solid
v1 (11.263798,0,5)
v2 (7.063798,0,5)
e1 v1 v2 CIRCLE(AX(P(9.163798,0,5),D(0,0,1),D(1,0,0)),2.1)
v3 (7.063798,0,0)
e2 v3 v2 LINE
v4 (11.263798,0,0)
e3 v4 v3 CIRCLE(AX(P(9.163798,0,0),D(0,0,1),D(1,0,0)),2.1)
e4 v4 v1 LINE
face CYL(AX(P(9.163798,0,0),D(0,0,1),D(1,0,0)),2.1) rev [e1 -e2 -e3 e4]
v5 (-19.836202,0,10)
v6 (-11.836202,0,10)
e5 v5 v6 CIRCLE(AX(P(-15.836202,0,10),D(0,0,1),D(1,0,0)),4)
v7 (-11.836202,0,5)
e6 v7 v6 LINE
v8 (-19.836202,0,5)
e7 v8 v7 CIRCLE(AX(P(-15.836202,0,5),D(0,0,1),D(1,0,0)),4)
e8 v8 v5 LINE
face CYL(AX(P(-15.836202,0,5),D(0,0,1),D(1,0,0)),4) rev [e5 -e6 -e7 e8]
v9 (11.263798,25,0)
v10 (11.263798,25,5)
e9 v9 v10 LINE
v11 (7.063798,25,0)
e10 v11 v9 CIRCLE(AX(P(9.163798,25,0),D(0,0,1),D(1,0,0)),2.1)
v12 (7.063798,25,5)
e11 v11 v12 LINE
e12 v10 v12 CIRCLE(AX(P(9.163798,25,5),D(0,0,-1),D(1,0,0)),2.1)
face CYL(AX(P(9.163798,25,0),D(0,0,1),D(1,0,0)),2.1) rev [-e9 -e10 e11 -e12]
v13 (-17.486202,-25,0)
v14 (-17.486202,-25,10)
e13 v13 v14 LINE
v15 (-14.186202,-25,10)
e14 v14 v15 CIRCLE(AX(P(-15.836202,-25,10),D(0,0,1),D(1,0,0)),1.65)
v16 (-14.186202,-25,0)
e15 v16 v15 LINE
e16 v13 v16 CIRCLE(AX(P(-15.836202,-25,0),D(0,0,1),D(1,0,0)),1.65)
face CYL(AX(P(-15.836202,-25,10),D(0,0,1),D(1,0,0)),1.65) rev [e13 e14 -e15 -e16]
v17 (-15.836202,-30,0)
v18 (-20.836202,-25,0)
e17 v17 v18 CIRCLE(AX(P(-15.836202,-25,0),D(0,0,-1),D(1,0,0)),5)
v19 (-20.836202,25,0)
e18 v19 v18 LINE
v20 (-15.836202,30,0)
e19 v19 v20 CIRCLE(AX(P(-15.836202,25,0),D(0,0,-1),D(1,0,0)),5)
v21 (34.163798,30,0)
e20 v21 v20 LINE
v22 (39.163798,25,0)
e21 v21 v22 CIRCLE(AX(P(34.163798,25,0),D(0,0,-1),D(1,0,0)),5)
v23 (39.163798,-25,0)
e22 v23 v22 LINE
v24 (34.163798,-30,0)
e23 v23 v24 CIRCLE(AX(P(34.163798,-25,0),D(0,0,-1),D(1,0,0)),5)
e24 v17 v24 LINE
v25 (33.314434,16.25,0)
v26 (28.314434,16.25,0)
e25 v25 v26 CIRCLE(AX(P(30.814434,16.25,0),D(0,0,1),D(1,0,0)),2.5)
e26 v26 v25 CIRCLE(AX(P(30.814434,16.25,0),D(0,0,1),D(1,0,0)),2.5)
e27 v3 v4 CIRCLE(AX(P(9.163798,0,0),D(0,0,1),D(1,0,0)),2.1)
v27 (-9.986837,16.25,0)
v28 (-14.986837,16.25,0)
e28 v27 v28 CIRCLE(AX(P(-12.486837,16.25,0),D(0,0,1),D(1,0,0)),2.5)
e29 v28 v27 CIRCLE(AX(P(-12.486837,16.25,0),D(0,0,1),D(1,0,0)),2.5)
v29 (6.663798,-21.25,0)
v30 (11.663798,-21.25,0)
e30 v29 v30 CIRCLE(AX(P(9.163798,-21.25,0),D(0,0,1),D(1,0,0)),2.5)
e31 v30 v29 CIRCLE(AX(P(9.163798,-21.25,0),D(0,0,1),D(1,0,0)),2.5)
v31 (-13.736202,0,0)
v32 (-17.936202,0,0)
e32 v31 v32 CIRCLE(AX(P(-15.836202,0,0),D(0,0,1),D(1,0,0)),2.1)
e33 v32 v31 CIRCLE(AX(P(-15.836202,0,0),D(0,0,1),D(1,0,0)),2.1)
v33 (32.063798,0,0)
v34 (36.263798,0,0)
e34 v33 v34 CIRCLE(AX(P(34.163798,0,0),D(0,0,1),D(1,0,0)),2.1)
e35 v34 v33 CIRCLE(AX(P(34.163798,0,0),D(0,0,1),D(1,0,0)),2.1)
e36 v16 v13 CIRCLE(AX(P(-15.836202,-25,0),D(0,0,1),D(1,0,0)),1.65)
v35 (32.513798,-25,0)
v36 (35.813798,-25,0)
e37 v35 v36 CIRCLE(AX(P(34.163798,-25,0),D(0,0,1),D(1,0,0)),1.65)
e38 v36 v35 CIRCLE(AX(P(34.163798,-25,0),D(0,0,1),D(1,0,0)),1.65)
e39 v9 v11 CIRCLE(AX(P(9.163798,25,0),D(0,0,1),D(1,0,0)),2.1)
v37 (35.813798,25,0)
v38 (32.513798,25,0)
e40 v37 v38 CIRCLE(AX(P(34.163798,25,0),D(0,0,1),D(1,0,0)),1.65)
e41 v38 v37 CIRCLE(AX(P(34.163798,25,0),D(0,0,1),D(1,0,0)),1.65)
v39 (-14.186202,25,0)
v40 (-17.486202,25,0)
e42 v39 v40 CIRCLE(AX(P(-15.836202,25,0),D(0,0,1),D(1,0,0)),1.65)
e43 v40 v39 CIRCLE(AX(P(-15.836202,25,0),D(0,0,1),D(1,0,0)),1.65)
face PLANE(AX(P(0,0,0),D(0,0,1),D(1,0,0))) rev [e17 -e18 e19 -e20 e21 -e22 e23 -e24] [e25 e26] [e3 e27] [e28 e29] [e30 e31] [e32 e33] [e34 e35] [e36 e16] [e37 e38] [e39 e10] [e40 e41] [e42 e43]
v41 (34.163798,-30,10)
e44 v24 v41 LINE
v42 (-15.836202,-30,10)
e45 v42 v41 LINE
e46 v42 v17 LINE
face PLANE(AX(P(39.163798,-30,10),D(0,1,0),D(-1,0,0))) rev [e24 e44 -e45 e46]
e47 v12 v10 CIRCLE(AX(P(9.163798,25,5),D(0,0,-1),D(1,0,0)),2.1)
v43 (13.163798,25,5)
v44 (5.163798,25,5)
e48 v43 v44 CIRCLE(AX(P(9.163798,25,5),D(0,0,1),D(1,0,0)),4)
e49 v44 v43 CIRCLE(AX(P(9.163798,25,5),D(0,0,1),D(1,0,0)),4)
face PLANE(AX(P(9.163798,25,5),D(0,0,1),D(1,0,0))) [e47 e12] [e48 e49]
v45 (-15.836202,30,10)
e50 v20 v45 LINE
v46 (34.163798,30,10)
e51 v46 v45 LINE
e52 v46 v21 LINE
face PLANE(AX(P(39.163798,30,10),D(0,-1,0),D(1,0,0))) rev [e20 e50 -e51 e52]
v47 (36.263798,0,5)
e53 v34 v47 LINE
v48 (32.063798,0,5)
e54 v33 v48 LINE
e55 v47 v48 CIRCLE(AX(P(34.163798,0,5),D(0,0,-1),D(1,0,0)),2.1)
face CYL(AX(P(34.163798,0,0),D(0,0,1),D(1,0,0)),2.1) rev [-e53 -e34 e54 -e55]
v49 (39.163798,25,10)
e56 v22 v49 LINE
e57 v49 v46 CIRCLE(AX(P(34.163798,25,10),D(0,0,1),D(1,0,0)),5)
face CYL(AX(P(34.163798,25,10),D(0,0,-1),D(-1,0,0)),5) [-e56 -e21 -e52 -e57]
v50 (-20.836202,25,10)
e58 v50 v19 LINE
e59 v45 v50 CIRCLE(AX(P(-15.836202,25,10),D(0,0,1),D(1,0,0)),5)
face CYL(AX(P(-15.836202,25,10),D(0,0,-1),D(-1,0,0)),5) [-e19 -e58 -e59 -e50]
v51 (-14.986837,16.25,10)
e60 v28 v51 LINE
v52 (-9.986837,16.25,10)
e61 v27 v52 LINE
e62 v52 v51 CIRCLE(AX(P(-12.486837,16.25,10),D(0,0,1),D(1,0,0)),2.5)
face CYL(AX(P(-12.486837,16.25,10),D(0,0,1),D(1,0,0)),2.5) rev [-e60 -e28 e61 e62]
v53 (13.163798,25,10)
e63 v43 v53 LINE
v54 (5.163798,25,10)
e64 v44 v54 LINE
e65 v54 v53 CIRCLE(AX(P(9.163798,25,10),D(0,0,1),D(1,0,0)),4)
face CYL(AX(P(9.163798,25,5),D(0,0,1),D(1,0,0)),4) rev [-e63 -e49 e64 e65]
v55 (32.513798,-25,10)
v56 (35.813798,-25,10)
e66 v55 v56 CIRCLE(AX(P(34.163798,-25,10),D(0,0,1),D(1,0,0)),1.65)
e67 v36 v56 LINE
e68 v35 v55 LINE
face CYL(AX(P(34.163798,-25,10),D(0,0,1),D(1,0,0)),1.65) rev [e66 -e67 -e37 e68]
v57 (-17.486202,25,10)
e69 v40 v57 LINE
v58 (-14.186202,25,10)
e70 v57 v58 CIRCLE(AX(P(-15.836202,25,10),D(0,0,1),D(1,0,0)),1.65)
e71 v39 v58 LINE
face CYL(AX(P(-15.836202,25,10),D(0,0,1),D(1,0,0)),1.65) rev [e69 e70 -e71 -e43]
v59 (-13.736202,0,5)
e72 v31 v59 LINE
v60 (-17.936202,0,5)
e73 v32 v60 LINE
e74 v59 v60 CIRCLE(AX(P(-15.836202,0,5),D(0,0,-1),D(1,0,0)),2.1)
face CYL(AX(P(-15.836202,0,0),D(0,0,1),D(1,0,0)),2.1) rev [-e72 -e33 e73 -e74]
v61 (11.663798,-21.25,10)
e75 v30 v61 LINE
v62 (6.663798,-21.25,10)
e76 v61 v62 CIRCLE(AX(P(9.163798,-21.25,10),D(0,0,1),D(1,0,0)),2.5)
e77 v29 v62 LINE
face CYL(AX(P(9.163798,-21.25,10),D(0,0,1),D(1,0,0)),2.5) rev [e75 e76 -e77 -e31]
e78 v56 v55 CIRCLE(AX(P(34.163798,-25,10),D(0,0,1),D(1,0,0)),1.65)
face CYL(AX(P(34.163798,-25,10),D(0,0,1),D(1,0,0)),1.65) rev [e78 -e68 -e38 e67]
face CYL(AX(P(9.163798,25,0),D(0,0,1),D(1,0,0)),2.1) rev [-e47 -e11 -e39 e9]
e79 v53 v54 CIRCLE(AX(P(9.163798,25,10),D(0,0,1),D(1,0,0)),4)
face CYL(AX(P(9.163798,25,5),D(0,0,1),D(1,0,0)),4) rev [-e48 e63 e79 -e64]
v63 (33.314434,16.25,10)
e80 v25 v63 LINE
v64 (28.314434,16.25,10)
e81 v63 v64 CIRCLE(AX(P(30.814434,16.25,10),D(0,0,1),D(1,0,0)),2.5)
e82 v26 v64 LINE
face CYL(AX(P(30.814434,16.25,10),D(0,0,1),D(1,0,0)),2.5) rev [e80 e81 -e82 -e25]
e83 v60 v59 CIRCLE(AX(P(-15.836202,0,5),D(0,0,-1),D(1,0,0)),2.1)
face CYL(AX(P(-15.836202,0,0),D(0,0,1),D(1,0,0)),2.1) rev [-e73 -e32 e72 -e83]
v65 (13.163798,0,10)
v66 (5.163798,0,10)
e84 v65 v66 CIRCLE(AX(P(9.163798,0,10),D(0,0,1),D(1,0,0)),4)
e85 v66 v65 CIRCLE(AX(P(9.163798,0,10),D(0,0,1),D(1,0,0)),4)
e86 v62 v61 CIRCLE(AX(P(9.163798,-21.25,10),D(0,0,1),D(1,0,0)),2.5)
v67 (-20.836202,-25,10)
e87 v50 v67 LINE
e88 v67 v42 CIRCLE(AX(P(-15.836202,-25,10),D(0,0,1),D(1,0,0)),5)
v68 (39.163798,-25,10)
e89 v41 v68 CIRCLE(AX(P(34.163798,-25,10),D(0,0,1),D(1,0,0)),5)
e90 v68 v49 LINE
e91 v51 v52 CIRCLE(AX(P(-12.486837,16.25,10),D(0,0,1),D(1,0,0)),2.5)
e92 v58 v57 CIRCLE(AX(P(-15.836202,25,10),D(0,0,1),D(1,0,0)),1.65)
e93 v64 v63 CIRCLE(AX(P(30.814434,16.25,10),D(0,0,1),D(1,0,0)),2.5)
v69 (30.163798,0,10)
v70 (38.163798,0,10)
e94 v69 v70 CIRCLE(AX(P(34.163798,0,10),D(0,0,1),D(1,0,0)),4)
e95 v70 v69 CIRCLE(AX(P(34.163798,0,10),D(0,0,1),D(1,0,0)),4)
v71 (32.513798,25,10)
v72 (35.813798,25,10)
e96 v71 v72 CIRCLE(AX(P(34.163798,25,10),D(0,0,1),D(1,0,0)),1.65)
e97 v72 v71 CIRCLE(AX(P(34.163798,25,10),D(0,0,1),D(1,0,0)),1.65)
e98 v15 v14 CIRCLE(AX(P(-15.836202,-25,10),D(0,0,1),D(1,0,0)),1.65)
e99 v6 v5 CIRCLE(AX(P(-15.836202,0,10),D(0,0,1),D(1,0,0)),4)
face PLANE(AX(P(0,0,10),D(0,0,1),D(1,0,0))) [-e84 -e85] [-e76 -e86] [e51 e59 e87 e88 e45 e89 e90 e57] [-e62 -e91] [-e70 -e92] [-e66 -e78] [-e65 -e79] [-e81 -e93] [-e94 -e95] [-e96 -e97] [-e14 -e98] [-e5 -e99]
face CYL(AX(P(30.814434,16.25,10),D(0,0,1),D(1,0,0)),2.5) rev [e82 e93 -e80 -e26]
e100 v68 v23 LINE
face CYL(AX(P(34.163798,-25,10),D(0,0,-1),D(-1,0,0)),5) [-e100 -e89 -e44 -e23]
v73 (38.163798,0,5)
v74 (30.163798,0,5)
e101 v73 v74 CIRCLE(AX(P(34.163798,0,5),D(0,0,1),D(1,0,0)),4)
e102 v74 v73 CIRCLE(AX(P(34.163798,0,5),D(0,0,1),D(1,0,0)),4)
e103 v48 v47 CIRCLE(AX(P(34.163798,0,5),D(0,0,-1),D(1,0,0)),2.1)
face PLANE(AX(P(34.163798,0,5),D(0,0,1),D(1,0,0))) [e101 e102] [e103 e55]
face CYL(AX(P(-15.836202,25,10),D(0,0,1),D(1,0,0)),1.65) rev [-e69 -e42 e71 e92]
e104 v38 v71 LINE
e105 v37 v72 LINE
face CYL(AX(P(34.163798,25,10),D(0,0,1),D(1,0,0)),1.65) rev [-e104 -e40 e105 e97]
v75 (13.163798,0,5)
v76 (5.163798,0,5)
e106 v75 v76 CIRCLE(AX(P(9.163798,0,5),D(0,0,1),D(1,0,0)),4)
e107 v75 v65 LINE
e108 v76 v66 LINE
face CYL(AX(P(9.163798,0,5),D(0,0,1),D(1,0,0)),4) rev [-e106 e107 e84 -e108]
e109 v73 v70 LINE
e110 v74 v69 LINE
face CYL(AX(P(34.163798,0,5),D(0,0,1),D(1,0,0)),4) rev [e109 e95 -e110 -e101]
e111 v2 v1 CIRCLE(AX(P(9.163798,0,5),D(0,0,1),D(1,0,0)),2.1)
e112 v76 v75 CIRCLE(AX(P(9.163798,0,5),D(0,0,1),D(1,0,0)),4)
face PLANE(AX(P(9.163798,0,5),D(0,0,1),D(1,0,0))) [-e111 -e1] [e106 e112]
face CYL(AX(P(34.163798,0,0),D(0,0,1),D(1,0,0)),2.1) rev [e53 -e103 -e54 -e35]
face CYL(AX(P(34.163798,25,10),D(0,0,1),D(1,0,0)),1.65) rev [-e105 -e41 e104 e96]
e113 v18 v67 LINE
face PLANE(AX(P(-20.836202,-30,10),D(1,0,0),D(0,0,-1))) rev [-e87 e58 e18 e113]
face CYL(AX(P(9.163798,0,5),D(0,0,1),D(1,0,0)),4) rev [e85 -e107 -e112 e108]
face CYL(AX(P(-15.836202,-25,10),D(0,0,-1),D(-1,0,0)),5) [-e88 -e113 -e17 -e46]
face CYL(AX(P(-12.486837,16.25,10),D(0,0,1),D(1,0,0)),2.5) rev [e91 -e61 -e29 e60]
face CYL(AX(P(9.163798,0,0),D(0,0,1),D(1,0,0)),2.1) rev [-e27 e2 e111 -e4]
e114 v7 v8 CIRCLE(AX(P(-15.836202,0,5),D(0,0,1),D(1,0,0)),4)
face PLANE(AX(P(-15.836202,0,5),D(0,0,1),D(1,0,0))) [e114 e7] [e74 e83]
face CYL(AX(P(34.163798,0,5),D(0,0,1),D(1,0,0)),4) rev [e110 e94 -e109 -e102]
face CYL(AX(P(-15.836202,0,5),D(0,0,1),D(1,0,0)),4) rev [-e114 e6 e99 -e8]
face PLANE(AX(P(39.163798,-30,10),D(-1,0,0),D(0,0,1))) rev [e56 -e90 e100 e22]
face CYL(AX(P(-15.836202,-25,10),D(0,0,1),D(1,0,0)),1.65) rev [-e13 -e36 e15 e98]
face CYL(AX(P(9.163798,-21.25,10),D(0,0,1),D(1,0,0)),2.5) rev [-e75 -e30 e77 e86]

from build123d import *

# Parameters (mm, degrees)
SKETCH1_W             = 60
SKETCH1_H             = 60
BOSS_EXTRUDE1_DEPTH   = 10
FILLET1_R             = 5
M6_TAPPED_HOLE1_D     = 5
M6_TAPPED_HOLE1_DEPTH = 15
M6_TAPPED_HOLE1_TIP   = 1.502151548
SKETCH8_R             = 2.1
CUT_EXTRUDE1_DEPTH    = 51.336896077
SKETCH9_R             = 4
CUT_EXTRUDE2_DEPTH    = 5
M4_TAPPED_HOLE1_D     = 3.3
M4_TAPPED_HOLE2_D     = 3.3
SKETCH15_R            = 4
CUT_EXTRUDE3_DEPTH    = 5
SKETCH16_R            = 2.1
CUT_EXTRUDE4_DEPTH    = 51.336896077


with BuildPart() as part:
    # Sketch1 → Boss-Extrude1 (new body)
    with BuildSketch(Plane.XY):
        with Locations((9.163798419, 0)):
            Rectangle(SKETCH1_W, SKETCH1_H)
    extrude(amount=BOSS_EXTRUDE1_DEPTH)

    # Fillet1
    fillet1_edges = [part.edges().sort_by_distance(p)[0] for p in [
        (-20.836201581, 30, 5),
        (39.163798419, 30, 5),
        (39.163798419, -30, 5),
        (-20.836201581, -30, 5),
    ]]
    fillet(fillet1_edges, radius=FILLET1_R)

    # M6 Tapped Hole1
    with Locations(Plane.XY.offset(10)):
        with Locations((9.163798419, -21.25), (30.814433514, 16.25), (-12.486836675, 16.25)):
            Hole(M6_TAPPED_HOLE1_D / 2, depth=M6_TAPPED_HOLE1_DEPTH)
            with Locations((0, 0, -(M6_TAPPED_HOLE1_DEPTH + M6_TAPPED_HOLE1_TIP / 2))):  # 118° drill point
                Cone(0, M6_TAPPED_HOLE1_D / 2, M6_TAPPED_HOLE1_TIP, mode=Mode.SUBTRACT)

    # Sketch8 → Cut-Extrude1 (cut, through all)
    with BuildSketch(Plane.XY.offset(10)):
        with Locations((9.163798419, 25)):
            Circle(SKETCH8_R)
        with Locations((34.163798419, 0)):
            Circle(SKETCH8_R)
        with Locations((-15.836201581, 0)):
            Circle(SKETCH8_R)
    extrude(amount=-CUT_EXTRUDE1_DEPTH, mode=Mode.SUBTRACT)

    # Sketch9 → Cut-Extrude2 (cut)
    with BuildSketch(Plane.XY.offset(10)):
        with Locations((-15.836201581, 0)):
            Circle(SKETCH9_R)
        with Locations((9.163798419, 25)):
            Circle(SKETCH9_R)
        with Locations((34.163798419, 0)):
            Circle(SKETCH9_R)
    extrude(amount=-CUT_EXTRUDE2_DEPTH, mode=Mode.SUBTRACT)

    # M4 Tapped Hole1 (through all)
    with Locations(Plane.XY.offset(10)):
        with Locations((-15.836201581, -25), (34.163798419, -25), (34.163798419, 25), (-15.836201581, 25)):
            Hole(M4_TAPPED_HOLE1_D / 2)

    # M4 Tapped Hole2 (through all)
    with Locations(Plane.XY.offset(10)):
        with Locations((9.163798419, 0)):
            Hole(M4_TAPPED_HOLE2_D / 2)

    # Sketch15 → Cut-Extrude3 (cut)
    with BuildSketch(Plane.XY.offset(10)):
        with Locations((9.163798419, 0)):
            Circle(SKETCH15_R)
    extrude(amount=-CUT_EXTRUDE3_DEPTH, mode=Mode.SUBTRACT)

    # Sketch16 → Cut-Extrude4 (cut, through all)
    with BuildSketch(Plane.XY.offset(10)):
        with Locations((9.163798419, 0)):
            Circle(SKETCH16_R)
    extrude(amount=-CUT_EXTRUDE4_DEPTH, mode=Mode.SUBTRACT)


solid = part.part
